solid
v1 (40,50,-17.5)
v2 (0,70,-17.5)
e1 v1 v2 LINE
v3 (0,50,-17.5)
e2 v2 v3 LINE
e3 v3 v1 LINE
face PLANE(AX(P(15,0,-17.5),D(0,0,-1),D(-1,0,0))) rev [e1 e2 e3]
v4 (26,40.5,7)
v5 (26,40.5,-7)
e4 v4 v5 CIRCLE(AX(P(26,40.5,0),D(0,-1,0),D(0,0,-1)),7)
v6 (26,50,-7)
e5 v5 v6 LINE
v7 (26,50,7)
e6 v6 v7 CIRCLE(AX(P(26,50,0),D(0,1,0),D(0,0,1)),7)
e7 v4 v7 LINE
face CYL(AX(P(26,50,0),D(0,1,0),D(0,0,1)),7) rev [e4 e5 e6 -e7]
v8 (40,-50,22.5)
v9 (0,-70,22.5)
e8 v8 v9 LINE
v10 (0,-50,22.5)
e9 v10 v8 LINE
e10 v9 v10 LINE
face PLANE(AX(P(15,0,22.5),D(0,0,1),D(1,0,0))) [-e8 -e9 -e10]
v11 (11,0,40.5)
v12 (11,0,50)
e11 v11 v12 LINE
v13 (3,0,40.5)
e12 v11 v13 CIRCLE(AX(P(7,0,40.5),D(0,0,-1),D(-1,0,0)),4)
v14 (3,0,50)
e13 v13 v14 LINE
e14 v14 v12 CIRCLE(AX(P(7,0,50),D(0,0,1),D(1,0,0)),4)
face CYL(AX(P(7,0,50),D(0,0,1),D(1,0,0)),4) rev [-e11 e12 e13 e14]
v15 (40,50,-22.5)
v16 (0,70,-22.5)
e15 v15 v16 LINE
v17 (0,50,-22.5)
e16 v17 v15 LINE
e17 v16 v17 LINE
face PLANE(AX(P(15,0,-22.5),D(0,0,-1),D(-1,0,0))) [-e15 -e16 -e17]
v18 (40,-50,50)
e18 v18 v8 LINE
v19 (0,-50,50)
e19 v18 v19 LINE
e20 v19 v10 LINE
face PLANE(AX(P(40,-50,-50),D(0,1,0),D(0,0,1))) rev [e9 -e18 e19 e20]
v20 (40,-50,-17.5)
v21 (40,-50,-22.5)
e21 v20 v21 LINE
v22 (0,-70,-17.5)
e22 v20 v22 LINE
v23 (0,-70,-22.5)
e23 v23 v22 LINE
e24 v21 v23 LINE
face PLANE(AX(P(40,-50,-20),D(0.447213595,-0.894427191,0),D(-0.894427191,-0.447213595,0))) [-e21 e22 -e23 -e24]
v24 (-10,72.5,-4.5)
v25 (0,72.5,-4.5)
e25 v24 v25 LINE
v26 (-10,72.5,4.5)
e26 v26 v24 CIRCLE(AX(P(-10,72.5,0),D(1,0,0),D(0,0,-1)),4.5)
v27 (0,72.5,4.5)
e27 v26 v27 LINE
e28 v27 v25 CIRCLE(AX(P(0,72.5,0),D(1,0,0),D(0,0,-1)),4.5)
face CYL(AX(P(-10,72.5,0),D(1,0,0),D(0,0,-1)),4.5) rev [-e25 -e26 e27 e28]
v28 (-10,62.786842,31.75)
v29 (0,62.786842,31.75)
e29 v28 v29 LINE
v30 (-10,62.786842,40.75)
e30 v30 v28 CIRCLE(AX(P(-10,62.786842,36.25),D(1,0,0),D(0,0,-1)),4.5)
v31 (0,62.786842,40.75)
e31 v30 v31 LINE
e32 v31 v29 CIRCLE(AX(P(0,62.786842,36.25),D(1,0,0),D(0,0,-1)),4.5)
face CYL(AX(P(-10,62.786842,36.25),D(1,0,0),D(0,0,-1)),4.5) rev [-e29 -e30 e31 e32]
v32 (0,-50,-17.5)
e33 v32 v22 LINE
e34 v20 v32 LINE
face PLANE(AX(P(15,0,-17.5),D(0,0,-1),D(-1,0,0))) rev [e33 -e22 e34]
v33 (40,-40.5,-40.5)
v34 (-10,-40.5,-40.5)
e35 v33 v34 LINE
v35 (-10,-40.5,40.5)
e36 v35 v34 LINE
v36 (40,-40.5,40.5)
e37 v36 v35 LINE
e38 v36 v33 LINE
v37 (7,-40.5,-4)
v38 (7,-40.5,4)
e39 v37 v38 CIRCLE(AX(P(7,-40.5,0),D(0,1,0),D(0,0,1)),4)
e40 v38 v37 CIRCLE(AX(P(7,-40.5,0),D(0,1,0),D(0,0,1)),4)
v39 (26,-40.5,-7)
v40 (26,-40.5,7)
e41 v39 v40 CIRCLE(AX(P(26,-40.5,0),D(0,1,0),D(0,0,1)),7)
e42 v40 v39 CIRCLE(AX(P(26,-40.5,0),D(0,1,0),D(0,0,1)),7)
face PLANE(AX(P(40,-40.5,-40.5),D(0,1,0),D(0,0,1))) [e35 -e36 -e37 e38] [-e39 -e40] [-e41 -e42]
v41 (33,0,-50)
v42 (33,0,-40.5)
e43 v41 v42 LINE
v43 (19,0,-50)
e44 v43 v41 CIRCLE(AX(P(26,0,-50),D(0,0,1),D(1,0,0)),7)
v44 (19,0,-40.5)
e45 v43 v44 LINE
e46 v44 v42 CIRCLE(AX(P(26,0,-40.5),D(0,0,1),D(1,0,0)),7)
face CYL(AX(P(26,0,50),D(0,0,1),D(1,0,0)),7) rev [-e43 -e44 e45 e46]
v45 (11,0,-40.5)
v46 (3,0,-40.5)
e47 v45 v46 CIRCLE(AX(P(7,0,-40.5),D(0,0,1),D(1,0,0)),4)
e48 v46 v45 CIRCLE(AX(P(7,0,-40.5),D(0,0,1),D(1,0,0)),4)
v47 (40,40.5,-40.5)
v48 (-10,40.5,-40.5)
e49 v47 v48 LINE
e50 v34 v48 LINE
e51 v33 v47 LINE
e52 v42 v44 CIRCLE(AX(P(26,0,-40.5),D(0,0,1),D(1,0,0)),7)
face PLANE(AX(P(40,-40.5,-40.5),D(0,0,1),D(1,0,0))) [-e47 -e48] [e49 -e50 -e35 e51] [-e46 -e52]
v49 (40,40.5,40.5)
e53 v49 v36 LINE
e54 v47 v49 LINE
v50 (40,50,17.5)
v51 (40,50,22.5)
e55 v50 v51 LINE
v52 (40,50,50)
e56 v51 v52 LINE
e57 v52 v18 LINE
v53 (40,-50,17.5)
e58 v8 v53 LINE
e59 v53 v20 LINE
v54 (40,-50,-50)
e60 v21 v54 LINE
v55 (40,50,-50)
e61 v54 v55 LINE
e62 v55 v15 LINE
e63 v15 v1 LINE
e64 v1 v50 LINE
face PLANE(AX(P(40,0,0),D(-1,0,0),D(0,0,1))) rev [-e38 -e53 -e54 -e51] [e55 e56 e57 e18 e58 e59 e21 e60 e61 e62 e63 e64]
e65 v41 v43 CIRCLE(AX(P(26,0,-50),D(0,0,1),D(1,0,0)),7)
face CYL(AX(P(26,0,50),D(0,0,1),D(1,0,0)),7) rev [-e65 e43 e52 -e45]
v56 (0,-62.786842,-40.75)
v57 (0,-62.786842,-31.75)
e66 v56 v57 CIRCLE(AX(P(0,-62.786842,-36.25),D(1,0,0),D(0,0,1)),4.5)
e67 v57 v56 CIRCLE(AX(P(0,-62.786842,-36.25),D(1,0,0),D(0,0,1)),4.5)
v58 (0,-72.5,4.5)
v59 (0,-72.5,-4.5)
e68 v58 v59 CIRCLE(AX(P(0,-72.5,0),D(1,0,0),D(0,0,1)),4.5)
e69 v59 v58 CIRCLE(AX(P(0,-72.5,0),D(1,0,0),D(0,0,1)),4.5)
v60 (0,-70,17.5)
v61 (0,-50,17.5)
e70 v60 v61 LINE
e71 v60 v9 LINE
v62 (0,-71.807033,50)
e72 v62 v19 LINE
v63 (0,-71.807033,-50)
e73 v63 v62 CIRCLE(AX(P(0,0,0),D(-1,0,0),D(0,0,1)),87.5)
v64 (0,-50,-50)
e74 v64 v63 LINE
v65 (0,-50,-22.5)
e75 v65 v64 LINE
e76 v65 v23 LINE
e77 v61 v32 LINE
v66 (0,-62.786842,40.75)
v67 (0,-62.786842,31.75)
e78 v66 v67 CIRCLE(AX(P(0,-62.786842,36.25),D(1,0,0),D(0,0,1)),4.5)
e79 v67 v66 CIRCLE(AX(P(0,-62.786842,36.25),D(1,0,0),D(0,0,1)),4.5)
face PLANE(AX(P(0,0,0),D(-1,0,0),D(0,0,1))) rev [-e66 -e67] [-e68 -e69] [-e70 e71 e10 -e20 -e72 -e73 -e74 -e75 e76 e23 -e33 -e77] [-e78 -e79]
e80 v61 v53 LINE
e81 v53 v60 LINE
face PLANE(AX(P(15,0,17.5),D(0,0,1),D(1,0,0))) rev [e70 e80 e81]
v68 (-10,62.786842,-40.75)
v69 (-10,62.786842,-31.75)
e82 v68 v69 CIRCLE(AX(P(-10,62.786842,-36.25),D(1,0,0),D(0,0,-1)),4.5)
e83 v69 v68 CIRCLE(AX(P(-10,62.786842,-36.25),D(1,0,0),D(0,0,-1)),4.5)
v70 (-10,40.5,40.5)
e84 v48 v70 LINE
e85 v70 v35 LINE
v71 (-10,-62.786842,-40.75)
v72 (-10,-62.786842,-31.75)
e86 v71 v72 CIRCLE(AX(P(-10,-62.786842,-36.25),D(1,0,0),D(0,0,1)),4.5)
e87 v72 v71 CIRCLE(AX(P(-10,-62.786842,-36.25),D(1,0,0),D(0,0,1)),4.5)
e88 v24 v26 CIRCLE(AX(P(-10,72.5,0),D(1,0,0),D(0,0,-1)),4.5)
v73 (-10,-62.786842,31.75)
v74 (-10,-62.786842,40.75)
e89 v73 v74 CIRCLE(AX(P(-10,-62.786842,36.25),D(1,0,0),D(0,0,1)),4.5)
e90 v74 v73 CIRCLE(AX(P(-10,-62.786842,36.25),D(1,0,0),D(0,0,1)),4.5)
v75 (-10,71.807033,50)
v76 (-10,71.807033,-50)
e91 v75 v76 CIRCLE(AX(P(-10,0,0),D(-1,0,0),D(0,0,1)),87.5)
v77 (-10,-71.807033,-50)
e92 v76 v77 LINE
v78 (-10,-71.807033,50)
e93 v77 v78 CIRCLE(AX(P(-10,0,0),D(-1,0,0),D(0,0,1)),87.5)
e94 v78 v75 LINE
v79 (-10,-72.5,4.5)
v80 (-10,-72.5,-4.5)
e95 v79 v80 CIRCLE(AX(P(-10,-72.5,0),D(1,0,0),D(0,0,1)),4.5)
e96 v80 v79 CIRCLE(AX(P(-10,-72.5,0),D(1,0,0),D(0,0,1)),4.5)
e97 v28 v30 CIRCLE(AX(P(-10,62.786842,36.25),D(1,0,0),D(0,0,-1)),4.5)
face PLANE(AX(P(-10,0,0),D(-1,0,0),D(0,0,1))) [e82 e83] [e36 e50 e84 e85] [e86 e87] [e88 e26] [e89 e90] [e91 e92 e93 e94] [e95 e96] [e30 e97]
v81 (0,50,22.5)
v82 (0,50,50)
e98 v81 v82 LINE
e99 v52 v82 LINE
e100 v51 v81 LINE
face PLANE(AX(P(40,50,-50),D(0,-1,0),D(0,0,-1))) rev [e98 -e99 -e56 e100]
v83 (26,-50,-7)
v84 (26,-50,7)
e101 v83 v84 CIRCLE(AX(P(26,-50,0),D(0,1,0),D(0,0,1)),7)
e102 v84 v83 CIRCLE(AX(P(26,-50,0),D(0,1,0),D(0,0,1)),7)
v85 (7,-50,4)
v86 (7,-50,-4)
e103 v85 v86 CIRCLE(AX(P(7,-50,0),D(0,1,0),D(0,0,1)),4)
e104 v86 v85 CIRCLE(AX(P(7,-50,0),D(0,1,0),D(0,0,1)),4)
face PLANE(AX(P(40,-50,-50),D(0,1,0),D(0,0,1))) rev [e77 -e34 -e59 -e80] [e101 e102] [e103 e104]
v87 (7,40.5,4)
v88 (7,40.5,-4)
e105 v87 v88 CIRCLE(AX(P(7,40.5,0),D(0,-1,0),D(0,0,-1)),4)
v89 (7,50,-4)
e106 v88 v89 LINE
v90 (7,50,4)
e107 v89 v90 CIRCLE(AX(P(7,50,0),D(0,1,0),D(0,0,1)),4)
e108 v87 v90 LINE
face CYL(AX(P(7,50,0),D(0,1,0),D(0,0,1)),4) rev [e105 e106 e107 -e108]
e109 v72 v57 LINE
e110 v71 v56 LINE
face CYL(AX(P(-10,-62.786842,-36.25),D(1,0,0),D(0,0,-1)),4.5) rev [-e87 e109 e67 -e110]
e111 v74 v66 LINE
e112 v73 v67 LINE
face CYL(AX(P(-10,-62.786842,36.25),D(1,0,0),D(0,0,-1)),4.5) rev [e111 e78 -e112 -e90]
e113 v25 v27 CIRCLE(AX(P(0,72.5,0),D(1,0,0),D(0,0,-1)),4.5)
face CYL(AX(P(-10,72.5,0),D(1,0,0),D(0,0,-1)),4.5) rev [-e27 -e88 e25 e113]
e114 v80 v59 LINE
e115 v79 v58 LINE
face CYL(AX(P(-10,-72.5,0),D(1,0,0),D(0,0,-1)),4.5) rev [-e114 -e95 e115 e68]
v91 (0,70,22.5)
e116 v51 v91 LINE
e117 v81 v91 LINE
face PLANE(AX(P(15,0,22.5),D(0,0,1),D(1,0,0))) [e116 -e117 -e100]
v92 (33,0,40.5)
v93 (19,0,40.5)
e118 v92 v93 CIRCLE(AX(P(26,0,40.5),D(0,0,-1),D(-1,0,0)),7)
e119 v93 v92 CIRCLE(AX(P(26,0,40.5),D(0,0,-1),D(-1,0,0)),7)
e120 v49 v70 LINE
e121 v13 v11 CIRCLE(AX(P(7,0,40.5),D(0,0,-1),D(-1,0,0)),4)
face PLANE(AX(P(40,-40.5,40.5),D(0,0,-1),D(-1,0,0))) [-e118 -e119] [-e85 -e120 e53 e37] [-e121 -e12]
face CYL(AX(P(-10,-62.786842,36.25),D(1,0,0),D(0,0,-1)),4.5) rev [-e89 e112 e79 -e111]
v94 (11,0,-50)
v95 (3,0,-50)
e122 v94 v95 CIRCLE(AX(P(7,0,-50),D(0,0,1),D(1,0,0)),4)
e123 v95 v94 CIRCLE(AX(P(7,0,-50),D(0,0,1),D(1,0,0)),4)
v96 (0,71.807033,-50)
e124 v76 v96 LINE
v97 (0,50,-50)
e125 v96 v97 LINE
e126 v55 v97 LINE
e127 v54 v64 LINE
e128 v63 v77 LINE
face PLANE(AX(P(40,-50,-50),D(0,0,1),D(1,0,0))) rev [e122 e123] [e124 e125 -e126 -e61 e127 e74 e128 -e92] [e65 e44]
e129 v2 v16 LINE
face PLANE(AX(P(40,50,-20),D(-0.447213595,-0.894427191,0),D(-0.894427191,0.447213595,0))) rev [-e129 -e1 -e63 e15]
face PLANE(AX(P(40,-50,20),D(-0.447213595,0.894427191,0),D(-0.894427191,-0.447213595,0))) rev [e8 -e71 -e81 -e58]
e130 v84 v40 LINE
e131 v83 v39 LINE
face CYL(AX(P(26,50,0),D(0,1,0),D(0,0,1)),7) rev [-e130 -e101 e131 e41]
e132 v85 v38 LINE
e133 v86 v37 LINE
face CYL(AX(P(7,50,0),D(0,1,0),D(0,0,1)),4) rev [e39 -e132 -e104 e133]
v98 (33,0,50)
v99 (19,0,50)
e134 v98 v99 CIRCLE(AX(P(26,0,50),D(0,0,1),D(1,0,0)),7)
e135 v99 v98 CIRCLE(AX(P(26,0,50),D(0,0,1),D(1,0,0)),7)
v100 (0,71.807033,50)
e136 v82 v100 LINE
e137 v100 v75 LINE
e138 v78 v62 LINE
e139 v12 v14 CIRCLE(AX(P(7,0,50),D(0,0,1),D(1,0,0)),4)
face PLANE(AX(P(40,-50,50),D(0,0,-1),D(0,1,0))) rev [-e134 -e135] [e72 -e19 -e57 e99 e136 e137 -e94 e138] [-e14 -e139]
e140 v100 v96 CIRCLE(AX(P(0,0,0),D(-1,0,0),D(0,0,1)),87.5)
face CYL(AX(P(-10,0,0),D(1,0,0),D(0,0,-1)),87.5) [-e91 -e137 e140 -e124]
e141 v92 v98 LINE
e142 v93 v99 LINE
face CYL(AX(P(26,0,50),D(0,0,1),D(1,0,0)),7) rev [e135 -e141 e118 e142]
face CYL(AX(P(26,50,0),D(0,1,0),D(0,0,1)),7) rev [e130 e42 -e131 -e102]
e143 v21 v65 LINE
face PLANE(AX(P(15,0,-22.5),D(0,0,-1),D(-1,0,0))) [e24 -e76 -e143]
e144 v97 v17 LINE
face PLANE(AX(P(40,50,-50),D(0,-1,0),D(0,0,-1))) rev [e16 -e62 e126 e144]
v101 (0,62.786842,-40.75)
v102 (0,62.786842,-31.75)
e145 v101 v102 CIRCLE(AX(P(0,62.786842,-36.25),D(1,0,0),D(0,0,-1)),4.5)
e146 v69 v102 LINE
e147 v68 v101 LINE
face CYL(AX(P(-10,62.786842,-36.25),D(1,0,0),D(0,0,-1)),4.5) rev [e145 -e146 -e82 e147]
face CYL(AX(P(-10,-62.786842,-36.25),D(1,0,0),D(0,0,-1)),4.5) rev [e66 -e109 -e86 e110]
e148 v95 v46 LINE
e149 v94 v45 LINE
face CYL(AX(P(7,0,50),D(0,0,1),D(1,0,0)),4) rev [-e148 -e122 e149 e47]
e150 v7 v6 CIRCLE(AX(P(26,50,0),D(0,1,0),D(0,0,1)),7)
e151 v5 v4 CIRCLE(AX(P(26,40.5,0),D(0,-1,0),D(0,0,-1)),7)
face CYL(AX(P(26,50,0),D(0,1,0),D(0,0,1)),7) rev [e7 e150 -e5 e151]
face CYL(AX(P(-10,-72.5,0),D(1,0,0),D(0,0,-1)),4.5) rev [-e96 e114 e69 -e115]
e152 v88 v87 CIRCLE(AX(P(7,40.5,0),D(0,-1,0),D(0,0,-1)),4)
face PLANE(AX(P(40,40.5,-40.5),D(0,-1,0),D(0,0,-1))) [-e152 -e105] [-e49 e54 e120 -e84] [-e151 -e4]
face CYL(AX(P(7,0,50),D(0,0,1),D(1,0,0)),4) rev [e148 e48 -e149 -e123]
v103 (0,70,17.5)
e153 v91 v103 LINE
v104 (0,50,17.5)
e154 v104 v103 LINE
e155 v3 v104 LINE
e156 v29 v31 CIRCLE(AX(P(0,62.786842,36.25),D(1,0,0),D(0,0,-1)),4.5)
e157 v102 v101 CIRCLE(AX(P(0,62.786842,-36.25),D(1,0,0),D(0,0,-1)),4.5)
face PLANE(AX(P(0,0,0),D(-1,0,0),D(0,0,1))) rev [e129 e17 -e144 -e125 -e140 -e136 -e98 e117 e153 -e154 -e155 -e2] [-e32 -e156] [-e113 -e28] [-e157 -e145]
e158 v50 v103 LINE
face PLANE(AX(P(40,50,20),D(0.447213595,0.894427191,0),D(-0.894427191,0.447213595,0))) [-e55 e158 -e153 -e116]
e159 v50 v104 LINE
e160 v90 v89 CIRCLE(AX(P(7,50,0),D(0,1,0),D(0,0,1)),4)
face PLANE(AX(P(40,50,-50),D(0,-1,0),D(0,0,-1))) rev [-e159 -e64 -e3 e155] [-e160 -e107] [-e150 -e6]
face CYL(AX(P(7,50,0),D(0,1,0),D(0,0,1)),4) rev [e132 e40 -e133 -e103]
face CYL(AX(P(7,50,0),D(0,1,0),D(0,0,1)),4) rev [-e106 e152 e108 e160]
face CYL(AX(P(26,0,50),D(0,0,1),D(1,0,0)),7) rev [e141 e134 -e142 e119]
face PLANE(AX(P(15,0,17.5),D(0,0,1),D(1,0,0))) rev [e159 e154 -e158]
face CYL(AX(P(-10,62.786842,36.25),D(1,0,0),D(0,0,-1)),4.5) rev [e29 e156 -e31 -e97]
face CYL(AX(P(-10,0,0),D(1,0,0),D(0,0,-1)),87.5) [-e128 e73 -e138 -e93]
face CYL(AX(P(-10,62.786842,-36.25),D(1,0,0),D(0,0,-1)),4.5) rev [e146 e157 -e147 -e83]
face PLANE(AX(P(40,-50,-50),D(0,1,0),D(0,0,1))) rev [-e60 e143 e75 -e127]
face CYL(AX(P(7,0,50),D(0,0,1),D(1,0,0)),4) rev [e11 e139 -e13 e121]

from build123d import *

# Parameters (mm, degrees)
SKETCH4_W               = 100
SKETCH4_H               = 100
SKETCH4_W_2             = 81
SKETCH4_H_2             = 81
BOSS_EXTRUDE1_DEPTH     = 40
SKETCH5_R               = 87.5
BOSS_EXTRUDE2_DEPTH     = 10
SKETCH6_OUTSIDE_W       = 227.498
SKETCH6_OUTSIDE_H       = 227.498
SKETCH6_OUTSIDE_W_2     = 100
SKETCH6_OUTSIDE_H_2     = 212.75110477
CUT_EXTRUDE1_DEPTH      = 10
SKETCH7_W               = 81
SKETCH7_H               = 81
CUT_EXTRUDE2_DEPTH      = 10
SKETCH8_R               = 4.5
CUT_EXTRUDE3_DEPTH      = 10
M16_TAPPED_HOLE1_D      = 14
M16_TAPPED_HOLE2_D      = 14
SIZE_MM_DOWEL_HOLE2_D   = 8
MM_2_D                  = 8
RIB2_REACH              = 120.98
SKETCH18_WALL_W         = 284.681440236
SKETCH18_WALL_H         = 5
MIRROR2_COPY_1_REACH    = 120.98
MIRROR2_COPY_1_SKETCH_W = 284.681440236
MIRROR2_COPY_1_SKETCH_H = 5


with BuildPart() as part:
    # Sketch4 → Boss-Extrude1 (new body)
    with BuildSketch(Plane(origin=(0, 0, 0), x_dir=(0, 0, -1), z_dir=(1, 0, 0))):
        Rectangle(SKETCH4_W, SKETCH4_H)
        Rectangle(SKETCH4_W_2, SKETCH4_H_2, mode=Mode.SUBTRACT)
    extrude(amount=BOSS_EXTRUDE1_DEPTH)

    # Sketch5 → Boss-Extrude2 (add)
    with BuildSketch(Plane.ZY):
        Circle(SKETCH5_R)
    extrude(amount=BOSS_EXTRUDE2_DEPTH)

    # Sketch6 outside → Cut-Extrude1 (cut)
    with BuildSketch(Plane.ZY.offset(10)):
        Rectangle(SKETCH6_OUTSIDE_W, SKETCH6_OUTSIDE_H)
        Rectangle(SKETCH6_OUTSIDE_W_2, SKETCH6_OUTSIDE_H_2, mode=Mode.SUBTRACT)
    extrude(amount=-CUT_EXTRUDE1_DEPTH, mode=Mode.SUBTRACT)

    # Sketch7 → Cut-Extrude2 (cut)
    with BuildSketch(Plane(origin=(0, 0, 0), x_dir=(0, 0, -1), z_dir=(1, 0, 0))):
        Rectangle(SKETCH7_W, SKETCH7_H)
    extrude(amount=-CUT_EXTRUDE2_DEPTH, mode=Mode.SUBTRACT)

    # Sketch8 → Cut-Extrude3 (cut)
    with BuildSketch(Plane(origin=(0, 0, 0), x_dir=(0, 0, -1), z_dir=(1, 0, 0))):
        with Locations((-36.25, 62.786841774)):
            Circle(SKETCH8_R)
        with Locations((0, 72.5)):
            Circle(SKETCH8_R)
        with Locations((36.25, 62.786841774)):
            Circle(SKETCH8_R)
        with Locations(Location((36.25, -62.786841774, 0), (0, 0, 180))):
            Circle(SKETCH8_R)
        with Locations(Location((0, -72.5, 0), (0, 0, 180))):
            Circle(SKETCH8_R)
        with Locations(Location((-36.25, -62.786841774, 0), (0, 0, 180))):
            Circle(SKETCH8_R)
    extrude(amount=-CUT_EXTRUDE3_DEPTH, mode=Mode.SUBTRACT)

    # M16 Tapped Hole1 (through all)
    with Locations(Plane.XY.offset(50)):
        with Locations((26, 0)):
            Hole(M16_TAPPED_HOLE1_D / 2)

    # M16 Tapped Hole2 (through all)
    with Locations(Plane(origin=(0, 50, 0), x_dir=(1, 0, 0), z_dir=(0, 1, 0))):
        with Locations((26, 0)):
            Hole(M16_TAPPED_HOLE2_D / 2)

    # Size mm Dowel Hole2 (through all)
    with Locations(Plane.XY.offset(50)):
        with Locations((7, 0)):
            Hole(SIZE_MM_DOWEL_HOLE2_D / 2)

    # 大小mm 暗销孔2 (through all)
    with Locations(Plane(origin=(0, 50, 0), x_dir=(1, 0, 0), z_dir=(0, 1, 0))):
        with Locations((7, 0)):
            Hole(MM_2_D / 2)

    # Sketch18 wall → Rib2 (add, up to next)
    with BuildSketch(Plane(origin=(20, 60, 20), x_dir=(-0.894427191, 0.4472135955, 0), z_dir=(-0.4472135955, -0.894427191, 0)), mode=Mode.PRIVATE) as rib2_sk1:
        Rectangle(SKETCH18_WALL_W, SKETCH18_WALL_H)
    rib2_tool1 = extrude(rib2_sk1.sketch, amount=RIB2_REACH, mode=Mode.PRIVATE) - part.part
    rib2 = rib2_tool1.solids().sort_by_distance((20, 60, 20))[0]
    add(rib2)

    # Mirror1: Rib2 across plane
    add(rib2.mirror(Plane.ZX))

    # Mirror2: Rib2 across plane
    add(rib2.mirror(Plane.XY))

    # Mirror2 copy 1 sketch → Mirror2 copy 1 (add, up to next)
    with BuildSketch(Plane(origin=(20, -60, -20), x_dir=(-0.894427191, -0.4472135955, 0), z_dir=(-0.4472135955, 0.894427191, 0)), mode=Mode.PRIVATE) as mirror2_copy_1_sk1:
        Rectangle(MIRROR2_COPY_1_SKETCH_W, MIRROR2_COPY_1_SKETCH_H)
    mirror2_copy_1_tool1 = extrude(mirror2_copy_1_sk1.sketch, amount=MIRROR2_COPY_1_REACH, mode=Mode.PRIVATE) - part.part
    add(mirror2_copy_1_tool1.solids().sort_by_distance((20, -60, -20))[0])


solid = part.part
